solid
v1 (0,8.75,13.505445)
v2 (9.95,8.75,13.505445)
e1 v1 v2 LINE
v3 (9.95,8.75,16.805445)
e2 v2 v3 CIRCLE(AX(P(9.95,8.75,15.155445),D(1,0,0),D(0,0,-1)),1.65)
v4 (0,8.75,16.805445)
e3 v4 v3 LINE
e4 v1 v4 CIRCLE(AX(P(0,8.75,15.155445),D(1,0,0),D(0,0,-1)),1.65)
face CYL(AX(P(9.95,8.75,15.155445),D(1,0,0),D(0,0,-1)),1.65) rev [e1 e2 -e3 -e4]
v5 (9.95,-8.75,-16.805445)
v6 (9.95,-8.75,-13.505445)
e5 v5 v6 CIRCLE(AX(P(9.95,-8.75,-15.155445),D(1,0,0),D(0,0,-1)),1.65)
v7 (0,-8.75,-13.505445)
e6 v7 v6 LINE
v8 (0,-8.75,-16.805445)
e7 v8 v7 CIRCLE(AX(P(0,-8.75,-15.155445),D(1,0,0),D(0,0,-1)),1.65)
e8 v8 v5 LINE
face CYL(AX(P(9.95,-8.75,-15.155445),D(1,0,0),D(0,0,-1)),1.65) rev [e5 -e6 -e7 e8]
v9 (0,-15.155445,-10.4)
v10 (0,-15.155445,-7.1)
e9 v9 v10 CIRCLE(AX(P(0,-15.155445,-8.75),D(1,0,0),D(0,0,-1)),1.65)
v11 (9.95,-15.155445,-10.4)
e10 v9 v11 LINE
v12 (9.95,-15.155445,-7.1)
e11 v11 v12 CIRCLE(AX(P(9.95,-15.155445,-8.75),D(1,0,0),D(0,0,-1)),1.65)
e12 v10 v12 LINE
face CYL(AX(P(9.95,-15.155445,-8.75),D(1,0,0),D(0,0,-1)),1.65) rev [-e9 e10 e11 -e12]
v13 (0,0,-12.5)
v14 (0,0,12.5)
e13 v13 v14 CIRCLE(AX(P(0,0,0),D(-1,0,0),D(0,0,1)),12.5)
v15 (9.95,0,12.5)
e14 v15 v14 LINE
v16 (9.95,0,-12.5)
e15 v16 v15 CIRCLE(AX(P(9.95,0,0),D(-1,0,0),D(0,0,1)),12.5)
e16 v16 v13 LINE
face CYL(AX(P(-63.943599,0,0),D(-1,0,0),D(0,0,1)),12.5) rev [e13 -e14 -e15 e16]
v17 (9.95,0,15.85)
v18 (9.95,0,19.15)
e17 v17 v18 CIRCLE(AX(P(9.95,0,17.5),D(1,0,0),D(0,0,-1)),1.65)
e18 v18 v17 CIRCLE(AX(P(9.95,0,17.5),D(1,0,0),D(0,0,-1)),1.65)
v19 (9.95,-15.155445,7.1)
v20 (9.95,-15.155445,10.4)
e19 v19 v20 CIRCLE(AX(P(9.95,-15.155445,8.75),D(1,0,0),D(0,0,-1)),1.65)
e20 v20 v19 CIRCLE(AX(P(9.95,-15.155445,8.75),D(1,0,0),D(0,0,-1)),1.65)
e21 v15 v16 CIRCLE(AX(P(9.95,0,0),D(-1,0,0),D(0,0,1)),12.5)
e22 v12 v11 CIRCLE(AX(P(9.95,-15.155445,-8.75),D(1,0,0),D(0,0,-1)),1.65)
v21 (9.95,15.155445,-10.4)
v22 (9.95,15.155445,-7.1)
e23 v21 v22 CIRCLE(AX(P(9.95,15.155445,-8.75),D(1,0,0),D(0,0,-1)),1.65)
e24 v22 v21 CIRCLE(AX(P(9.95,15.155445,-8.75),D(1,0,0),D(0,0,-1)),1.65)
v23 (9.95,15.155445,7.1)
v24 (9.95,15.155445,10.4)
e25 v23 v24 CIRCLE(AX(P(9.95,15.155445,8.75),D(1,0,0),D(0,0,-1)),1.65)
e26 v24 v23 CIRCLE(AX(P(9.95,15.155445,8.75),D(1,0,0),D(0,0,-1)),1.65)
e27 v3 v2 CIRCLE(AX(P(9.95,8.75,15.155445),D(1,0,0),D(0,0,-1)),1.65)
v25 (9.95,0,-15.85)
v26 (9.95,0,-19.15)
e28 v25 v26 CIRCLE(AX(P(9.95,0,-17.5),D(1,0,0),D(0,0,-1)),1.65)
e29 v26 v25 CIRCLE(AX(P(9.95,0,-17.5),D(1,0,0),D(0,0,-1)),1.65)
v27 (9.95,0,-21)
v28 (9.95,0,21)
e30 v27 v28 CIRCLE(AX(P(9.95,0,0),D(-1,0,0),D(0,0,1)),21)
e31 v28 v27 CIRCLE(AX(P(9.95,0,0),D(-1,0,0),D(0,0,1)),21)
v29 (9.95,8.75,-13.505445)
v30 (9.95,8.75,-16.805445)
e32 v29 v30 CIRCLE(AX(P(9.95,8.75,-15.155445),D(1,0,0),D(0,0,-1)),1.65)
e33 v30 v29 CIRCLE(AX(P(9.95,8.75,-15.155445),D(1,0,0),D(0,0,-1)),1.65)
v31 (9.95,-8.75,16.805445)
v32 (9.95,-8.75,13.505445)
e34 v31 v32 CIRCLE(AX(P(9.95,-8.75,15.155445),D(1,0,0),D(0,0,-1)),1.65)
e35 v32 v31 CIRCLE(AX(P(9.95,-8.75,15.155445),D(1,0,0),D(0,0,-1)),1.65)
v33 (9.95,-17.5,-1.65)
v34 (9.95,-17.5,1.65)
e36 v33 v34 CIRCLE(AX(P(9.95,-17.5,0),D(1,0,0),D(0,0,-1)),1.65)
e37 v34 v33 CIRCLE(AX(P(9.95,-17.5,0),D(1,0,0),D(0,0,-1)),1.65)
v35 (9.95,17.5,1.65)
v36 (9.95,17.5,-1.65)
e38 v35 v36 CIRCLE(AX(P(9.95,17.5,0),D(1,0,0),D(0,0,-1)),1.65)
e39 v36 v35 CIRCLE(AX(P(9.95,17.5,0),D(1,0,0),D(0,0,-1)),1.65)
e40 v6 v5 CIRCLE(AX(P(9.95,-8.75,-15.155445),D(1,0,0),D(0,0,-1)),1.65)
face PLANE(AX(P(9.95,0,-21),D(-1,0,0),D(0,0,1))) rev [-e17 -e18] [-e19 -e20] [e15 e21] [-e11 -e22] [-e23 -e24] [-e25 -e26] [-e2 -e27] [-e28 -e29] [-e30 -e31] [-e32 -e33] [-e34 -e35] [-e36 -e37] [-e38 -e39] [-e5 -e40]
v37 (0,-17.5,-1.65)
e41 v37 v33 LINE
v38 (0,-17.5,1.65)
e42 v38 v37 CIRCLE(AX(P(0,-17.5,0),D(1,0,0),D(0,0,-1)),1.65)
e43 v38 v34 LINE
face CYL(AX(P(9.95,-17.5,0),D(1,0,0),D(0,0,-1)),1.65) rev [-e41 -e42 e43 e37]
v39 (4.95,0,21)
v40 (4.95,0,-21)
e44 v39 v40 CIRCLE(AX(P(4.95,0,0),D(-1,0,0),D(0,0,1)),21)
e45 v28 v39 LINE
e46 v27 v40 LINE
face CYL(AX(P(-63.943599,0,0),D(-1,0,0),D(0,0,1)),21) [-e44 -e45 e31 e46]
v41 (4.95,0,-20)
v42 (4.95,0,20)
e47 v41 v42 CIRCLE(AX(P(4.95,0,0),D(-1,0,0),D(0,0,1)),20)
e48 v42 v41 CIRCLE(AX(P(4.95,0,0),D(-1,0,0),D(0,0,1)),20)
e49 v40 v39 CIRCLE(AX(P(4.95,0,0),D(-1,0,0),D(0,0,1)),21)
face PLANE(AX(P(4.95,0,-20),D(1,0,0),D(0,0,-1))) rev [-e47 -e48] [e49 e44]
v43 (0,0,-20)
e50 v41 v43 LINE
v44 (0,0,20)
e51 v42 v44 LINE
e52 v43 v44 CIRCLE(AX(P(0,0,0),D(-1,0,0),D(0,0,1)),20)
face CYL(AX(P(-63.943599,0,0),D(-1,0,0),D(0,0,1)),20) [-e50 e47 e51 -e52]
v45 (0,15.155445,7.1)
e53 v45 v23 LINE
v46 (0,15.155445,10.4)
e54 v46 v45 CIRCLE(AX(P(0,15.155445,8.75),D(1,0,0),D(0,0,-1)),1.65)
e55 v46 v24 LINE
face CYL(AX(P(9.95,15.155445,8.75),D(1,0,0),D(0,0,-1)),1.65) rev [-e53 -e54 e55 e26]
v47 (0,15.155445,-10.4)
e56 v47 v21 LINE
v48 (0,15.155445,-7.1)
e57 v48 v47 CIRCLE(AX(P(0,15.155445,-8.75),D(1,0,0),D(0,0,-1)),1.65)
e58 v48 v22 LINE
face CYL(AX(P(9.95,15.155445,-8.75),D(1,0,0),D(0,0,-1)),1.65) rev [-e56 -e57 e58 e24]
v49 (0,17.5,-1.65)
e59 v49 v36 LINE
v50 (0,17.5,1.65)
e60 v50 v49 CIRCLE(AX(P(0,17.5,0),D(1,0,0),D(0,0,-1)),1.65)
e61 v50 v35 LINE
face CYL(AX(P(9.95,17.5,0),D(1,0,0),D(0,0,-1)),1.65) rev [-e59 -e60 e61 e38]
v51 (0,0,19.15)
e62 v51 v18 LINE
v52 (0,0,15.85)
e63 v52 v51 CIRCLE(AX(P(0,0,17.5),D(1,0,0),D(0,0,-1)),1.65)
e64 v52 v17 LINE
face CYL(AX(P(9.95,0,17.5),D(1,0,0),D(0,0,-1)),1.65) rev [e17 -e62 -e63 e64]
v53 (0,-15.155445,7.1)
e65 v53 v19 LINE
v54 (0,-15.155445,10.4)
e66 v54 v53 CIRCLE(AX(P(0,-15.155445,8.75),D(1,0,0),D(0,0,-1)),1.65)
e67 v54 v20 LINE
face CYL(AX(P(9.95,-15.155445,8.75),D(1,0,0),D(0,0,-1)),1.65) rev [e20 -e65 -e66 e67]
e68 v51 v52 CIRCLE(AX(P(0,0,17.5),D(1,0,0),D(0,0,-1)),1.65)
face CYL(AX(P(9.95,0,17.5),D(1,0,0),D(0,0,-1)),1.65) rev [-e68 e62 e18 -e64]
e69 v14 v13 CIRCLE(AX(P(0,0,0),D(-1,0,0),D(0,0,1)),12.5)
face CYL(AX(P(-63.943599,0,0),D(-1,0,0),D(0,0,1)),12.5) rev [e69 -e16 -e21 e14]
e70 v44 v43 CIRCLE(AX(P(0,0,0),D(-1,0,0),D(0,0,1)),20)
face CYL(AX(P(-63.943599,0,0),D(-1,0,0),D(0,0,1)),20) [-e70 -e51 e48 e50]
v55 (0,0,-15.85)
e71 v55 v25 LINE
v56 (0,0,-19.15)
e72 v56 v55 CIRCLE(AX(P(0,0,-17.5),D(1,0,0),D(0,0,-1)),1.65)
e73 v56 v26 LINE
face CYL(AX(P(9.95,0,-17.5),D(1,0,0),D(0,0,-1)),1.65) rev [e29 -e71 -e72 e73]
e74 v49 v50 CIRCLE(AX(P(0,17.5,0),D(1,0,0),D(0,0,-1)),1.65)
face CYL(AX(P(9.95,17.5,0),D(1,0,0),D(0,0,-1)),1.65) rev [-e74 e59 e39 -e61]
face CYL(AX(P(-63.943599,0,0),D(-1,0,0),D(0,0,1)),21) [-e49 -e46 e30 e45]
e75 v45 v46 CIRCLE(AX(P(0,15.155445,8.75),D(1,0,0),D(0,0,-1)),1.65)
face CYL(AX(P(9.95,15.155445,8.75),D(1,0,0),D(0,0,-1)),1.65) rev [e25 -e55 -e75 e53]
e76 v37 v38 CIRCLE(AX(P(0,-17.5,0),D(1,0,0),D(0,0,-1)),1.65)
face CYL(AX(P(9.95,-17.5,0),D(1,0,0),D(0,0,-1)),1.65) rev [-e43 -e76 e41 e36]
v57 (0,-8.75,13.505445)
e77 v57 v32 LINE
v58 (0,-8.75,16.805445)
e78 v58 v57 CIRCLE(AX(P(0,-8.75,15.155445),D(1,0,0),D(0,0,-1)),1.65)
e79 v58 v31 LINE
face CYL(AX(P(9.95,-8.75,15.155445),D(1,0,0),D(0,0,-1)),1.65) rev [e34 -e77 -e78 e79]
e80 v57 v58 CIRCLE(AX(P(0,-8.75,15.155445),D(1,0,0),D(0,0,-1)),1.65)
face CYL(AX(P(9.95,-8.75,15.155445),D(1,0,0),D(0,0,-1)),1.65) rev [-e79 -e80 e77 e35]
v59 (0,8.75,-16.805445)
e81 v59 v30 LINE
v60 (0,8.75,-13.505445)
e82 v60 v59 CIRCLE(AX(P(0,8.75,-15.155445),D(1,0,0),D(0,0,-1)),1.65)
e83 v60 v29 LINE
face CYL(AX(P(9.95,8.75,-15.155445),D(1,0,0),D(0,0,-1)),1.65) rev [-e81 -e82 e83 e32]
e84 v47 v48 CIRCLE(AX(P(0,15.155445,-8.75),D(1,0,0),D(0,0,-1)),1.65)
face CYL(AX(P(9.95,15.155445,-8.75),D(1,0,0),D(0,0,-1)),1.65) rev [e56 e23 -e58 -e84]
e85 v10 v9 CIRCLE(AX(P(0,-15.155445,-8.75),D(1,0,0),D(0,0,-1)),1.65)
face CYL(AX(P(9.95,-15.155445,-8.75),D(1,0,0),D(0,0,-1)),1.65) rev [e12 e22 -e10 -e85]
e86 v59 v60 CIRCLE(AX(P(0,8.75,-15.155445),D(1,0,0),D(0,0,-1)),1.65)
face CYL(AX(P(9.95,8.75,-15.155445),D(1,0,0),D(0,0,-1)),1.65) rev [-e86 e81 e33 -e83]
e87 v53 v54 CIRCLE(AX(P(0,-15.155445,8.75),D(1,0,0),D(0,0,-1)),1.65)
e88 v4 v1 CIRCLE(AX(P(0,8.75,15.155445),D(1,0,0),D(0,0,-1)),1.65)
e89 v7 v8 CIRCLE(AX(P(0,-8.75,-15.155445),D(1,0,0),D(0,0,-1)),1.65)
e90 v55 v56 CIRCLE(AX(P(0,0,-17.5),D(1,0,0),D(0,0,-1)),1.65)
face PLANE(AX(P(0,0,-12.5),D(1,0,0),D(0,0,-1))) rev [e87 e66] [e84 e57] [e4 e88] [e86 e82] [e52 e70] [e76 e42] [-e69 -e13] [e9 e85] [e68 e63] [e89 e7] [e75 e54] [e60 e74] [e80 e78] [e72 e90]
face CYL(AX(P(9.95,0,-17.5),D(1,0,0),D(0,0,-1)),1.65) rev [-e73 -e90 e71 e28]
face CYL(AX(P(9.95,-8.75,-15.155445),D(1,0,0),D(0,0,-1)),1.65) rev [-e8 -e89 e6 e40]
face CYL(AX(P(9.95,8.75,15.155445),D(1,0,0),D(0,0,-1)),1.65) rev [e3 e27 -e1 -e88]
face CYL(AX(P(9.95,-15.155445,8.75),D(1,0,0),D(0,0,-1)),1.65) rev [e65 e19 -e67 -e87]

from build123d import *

# Parameters (mm, degrees)
HOLE_WIZARD_M4_1_D = 3.3


with BuildPart() as part:
    # 草图1 → 旋转1 (revolve)
    with BuildSketch(Plane(origin=(0, 0, 0), x_dir=(1, 0, 0), z_dir=(0, 1, 0)), mode=Mode.PRIVATE) as revolve_1_sk:
        Polygon((0, 12.5), (0, 20), (4.95, 20), (4.95, 21), (9.95, 21), (9.95, 12.5), align=None)
    revolve(revolve_1_sk.sketch.rotate(Axis((-63.943599205, 0, 0), (1, 0, 0)), 180), axis=Axis((-63.943599205, 0, 0), (1, 0, 0)))

    # M4 螺纹孔1 (through all)
    with Locations(Plane(origin=(9.95, 0, 0), x_dir=(0, 0, -1), z_dir=(1, 0, 0))):
        with Locations((0, 0), (0, 17.5), (8.75, 15.155444566), (15.155444566, 8.75), (17.5, 0), (15.155444566, -8.75), (8.75, -15.155444566), (0, -17.5), (-8.75, -15.155444566), (-15.155444566, -8.75), (-17.5, 0), (-15.155444566, 8.75), (-8.75, 15.155444566)):
            Hole(HOLE_WIZARD_M4_1_D / 2)


solid = part.part
